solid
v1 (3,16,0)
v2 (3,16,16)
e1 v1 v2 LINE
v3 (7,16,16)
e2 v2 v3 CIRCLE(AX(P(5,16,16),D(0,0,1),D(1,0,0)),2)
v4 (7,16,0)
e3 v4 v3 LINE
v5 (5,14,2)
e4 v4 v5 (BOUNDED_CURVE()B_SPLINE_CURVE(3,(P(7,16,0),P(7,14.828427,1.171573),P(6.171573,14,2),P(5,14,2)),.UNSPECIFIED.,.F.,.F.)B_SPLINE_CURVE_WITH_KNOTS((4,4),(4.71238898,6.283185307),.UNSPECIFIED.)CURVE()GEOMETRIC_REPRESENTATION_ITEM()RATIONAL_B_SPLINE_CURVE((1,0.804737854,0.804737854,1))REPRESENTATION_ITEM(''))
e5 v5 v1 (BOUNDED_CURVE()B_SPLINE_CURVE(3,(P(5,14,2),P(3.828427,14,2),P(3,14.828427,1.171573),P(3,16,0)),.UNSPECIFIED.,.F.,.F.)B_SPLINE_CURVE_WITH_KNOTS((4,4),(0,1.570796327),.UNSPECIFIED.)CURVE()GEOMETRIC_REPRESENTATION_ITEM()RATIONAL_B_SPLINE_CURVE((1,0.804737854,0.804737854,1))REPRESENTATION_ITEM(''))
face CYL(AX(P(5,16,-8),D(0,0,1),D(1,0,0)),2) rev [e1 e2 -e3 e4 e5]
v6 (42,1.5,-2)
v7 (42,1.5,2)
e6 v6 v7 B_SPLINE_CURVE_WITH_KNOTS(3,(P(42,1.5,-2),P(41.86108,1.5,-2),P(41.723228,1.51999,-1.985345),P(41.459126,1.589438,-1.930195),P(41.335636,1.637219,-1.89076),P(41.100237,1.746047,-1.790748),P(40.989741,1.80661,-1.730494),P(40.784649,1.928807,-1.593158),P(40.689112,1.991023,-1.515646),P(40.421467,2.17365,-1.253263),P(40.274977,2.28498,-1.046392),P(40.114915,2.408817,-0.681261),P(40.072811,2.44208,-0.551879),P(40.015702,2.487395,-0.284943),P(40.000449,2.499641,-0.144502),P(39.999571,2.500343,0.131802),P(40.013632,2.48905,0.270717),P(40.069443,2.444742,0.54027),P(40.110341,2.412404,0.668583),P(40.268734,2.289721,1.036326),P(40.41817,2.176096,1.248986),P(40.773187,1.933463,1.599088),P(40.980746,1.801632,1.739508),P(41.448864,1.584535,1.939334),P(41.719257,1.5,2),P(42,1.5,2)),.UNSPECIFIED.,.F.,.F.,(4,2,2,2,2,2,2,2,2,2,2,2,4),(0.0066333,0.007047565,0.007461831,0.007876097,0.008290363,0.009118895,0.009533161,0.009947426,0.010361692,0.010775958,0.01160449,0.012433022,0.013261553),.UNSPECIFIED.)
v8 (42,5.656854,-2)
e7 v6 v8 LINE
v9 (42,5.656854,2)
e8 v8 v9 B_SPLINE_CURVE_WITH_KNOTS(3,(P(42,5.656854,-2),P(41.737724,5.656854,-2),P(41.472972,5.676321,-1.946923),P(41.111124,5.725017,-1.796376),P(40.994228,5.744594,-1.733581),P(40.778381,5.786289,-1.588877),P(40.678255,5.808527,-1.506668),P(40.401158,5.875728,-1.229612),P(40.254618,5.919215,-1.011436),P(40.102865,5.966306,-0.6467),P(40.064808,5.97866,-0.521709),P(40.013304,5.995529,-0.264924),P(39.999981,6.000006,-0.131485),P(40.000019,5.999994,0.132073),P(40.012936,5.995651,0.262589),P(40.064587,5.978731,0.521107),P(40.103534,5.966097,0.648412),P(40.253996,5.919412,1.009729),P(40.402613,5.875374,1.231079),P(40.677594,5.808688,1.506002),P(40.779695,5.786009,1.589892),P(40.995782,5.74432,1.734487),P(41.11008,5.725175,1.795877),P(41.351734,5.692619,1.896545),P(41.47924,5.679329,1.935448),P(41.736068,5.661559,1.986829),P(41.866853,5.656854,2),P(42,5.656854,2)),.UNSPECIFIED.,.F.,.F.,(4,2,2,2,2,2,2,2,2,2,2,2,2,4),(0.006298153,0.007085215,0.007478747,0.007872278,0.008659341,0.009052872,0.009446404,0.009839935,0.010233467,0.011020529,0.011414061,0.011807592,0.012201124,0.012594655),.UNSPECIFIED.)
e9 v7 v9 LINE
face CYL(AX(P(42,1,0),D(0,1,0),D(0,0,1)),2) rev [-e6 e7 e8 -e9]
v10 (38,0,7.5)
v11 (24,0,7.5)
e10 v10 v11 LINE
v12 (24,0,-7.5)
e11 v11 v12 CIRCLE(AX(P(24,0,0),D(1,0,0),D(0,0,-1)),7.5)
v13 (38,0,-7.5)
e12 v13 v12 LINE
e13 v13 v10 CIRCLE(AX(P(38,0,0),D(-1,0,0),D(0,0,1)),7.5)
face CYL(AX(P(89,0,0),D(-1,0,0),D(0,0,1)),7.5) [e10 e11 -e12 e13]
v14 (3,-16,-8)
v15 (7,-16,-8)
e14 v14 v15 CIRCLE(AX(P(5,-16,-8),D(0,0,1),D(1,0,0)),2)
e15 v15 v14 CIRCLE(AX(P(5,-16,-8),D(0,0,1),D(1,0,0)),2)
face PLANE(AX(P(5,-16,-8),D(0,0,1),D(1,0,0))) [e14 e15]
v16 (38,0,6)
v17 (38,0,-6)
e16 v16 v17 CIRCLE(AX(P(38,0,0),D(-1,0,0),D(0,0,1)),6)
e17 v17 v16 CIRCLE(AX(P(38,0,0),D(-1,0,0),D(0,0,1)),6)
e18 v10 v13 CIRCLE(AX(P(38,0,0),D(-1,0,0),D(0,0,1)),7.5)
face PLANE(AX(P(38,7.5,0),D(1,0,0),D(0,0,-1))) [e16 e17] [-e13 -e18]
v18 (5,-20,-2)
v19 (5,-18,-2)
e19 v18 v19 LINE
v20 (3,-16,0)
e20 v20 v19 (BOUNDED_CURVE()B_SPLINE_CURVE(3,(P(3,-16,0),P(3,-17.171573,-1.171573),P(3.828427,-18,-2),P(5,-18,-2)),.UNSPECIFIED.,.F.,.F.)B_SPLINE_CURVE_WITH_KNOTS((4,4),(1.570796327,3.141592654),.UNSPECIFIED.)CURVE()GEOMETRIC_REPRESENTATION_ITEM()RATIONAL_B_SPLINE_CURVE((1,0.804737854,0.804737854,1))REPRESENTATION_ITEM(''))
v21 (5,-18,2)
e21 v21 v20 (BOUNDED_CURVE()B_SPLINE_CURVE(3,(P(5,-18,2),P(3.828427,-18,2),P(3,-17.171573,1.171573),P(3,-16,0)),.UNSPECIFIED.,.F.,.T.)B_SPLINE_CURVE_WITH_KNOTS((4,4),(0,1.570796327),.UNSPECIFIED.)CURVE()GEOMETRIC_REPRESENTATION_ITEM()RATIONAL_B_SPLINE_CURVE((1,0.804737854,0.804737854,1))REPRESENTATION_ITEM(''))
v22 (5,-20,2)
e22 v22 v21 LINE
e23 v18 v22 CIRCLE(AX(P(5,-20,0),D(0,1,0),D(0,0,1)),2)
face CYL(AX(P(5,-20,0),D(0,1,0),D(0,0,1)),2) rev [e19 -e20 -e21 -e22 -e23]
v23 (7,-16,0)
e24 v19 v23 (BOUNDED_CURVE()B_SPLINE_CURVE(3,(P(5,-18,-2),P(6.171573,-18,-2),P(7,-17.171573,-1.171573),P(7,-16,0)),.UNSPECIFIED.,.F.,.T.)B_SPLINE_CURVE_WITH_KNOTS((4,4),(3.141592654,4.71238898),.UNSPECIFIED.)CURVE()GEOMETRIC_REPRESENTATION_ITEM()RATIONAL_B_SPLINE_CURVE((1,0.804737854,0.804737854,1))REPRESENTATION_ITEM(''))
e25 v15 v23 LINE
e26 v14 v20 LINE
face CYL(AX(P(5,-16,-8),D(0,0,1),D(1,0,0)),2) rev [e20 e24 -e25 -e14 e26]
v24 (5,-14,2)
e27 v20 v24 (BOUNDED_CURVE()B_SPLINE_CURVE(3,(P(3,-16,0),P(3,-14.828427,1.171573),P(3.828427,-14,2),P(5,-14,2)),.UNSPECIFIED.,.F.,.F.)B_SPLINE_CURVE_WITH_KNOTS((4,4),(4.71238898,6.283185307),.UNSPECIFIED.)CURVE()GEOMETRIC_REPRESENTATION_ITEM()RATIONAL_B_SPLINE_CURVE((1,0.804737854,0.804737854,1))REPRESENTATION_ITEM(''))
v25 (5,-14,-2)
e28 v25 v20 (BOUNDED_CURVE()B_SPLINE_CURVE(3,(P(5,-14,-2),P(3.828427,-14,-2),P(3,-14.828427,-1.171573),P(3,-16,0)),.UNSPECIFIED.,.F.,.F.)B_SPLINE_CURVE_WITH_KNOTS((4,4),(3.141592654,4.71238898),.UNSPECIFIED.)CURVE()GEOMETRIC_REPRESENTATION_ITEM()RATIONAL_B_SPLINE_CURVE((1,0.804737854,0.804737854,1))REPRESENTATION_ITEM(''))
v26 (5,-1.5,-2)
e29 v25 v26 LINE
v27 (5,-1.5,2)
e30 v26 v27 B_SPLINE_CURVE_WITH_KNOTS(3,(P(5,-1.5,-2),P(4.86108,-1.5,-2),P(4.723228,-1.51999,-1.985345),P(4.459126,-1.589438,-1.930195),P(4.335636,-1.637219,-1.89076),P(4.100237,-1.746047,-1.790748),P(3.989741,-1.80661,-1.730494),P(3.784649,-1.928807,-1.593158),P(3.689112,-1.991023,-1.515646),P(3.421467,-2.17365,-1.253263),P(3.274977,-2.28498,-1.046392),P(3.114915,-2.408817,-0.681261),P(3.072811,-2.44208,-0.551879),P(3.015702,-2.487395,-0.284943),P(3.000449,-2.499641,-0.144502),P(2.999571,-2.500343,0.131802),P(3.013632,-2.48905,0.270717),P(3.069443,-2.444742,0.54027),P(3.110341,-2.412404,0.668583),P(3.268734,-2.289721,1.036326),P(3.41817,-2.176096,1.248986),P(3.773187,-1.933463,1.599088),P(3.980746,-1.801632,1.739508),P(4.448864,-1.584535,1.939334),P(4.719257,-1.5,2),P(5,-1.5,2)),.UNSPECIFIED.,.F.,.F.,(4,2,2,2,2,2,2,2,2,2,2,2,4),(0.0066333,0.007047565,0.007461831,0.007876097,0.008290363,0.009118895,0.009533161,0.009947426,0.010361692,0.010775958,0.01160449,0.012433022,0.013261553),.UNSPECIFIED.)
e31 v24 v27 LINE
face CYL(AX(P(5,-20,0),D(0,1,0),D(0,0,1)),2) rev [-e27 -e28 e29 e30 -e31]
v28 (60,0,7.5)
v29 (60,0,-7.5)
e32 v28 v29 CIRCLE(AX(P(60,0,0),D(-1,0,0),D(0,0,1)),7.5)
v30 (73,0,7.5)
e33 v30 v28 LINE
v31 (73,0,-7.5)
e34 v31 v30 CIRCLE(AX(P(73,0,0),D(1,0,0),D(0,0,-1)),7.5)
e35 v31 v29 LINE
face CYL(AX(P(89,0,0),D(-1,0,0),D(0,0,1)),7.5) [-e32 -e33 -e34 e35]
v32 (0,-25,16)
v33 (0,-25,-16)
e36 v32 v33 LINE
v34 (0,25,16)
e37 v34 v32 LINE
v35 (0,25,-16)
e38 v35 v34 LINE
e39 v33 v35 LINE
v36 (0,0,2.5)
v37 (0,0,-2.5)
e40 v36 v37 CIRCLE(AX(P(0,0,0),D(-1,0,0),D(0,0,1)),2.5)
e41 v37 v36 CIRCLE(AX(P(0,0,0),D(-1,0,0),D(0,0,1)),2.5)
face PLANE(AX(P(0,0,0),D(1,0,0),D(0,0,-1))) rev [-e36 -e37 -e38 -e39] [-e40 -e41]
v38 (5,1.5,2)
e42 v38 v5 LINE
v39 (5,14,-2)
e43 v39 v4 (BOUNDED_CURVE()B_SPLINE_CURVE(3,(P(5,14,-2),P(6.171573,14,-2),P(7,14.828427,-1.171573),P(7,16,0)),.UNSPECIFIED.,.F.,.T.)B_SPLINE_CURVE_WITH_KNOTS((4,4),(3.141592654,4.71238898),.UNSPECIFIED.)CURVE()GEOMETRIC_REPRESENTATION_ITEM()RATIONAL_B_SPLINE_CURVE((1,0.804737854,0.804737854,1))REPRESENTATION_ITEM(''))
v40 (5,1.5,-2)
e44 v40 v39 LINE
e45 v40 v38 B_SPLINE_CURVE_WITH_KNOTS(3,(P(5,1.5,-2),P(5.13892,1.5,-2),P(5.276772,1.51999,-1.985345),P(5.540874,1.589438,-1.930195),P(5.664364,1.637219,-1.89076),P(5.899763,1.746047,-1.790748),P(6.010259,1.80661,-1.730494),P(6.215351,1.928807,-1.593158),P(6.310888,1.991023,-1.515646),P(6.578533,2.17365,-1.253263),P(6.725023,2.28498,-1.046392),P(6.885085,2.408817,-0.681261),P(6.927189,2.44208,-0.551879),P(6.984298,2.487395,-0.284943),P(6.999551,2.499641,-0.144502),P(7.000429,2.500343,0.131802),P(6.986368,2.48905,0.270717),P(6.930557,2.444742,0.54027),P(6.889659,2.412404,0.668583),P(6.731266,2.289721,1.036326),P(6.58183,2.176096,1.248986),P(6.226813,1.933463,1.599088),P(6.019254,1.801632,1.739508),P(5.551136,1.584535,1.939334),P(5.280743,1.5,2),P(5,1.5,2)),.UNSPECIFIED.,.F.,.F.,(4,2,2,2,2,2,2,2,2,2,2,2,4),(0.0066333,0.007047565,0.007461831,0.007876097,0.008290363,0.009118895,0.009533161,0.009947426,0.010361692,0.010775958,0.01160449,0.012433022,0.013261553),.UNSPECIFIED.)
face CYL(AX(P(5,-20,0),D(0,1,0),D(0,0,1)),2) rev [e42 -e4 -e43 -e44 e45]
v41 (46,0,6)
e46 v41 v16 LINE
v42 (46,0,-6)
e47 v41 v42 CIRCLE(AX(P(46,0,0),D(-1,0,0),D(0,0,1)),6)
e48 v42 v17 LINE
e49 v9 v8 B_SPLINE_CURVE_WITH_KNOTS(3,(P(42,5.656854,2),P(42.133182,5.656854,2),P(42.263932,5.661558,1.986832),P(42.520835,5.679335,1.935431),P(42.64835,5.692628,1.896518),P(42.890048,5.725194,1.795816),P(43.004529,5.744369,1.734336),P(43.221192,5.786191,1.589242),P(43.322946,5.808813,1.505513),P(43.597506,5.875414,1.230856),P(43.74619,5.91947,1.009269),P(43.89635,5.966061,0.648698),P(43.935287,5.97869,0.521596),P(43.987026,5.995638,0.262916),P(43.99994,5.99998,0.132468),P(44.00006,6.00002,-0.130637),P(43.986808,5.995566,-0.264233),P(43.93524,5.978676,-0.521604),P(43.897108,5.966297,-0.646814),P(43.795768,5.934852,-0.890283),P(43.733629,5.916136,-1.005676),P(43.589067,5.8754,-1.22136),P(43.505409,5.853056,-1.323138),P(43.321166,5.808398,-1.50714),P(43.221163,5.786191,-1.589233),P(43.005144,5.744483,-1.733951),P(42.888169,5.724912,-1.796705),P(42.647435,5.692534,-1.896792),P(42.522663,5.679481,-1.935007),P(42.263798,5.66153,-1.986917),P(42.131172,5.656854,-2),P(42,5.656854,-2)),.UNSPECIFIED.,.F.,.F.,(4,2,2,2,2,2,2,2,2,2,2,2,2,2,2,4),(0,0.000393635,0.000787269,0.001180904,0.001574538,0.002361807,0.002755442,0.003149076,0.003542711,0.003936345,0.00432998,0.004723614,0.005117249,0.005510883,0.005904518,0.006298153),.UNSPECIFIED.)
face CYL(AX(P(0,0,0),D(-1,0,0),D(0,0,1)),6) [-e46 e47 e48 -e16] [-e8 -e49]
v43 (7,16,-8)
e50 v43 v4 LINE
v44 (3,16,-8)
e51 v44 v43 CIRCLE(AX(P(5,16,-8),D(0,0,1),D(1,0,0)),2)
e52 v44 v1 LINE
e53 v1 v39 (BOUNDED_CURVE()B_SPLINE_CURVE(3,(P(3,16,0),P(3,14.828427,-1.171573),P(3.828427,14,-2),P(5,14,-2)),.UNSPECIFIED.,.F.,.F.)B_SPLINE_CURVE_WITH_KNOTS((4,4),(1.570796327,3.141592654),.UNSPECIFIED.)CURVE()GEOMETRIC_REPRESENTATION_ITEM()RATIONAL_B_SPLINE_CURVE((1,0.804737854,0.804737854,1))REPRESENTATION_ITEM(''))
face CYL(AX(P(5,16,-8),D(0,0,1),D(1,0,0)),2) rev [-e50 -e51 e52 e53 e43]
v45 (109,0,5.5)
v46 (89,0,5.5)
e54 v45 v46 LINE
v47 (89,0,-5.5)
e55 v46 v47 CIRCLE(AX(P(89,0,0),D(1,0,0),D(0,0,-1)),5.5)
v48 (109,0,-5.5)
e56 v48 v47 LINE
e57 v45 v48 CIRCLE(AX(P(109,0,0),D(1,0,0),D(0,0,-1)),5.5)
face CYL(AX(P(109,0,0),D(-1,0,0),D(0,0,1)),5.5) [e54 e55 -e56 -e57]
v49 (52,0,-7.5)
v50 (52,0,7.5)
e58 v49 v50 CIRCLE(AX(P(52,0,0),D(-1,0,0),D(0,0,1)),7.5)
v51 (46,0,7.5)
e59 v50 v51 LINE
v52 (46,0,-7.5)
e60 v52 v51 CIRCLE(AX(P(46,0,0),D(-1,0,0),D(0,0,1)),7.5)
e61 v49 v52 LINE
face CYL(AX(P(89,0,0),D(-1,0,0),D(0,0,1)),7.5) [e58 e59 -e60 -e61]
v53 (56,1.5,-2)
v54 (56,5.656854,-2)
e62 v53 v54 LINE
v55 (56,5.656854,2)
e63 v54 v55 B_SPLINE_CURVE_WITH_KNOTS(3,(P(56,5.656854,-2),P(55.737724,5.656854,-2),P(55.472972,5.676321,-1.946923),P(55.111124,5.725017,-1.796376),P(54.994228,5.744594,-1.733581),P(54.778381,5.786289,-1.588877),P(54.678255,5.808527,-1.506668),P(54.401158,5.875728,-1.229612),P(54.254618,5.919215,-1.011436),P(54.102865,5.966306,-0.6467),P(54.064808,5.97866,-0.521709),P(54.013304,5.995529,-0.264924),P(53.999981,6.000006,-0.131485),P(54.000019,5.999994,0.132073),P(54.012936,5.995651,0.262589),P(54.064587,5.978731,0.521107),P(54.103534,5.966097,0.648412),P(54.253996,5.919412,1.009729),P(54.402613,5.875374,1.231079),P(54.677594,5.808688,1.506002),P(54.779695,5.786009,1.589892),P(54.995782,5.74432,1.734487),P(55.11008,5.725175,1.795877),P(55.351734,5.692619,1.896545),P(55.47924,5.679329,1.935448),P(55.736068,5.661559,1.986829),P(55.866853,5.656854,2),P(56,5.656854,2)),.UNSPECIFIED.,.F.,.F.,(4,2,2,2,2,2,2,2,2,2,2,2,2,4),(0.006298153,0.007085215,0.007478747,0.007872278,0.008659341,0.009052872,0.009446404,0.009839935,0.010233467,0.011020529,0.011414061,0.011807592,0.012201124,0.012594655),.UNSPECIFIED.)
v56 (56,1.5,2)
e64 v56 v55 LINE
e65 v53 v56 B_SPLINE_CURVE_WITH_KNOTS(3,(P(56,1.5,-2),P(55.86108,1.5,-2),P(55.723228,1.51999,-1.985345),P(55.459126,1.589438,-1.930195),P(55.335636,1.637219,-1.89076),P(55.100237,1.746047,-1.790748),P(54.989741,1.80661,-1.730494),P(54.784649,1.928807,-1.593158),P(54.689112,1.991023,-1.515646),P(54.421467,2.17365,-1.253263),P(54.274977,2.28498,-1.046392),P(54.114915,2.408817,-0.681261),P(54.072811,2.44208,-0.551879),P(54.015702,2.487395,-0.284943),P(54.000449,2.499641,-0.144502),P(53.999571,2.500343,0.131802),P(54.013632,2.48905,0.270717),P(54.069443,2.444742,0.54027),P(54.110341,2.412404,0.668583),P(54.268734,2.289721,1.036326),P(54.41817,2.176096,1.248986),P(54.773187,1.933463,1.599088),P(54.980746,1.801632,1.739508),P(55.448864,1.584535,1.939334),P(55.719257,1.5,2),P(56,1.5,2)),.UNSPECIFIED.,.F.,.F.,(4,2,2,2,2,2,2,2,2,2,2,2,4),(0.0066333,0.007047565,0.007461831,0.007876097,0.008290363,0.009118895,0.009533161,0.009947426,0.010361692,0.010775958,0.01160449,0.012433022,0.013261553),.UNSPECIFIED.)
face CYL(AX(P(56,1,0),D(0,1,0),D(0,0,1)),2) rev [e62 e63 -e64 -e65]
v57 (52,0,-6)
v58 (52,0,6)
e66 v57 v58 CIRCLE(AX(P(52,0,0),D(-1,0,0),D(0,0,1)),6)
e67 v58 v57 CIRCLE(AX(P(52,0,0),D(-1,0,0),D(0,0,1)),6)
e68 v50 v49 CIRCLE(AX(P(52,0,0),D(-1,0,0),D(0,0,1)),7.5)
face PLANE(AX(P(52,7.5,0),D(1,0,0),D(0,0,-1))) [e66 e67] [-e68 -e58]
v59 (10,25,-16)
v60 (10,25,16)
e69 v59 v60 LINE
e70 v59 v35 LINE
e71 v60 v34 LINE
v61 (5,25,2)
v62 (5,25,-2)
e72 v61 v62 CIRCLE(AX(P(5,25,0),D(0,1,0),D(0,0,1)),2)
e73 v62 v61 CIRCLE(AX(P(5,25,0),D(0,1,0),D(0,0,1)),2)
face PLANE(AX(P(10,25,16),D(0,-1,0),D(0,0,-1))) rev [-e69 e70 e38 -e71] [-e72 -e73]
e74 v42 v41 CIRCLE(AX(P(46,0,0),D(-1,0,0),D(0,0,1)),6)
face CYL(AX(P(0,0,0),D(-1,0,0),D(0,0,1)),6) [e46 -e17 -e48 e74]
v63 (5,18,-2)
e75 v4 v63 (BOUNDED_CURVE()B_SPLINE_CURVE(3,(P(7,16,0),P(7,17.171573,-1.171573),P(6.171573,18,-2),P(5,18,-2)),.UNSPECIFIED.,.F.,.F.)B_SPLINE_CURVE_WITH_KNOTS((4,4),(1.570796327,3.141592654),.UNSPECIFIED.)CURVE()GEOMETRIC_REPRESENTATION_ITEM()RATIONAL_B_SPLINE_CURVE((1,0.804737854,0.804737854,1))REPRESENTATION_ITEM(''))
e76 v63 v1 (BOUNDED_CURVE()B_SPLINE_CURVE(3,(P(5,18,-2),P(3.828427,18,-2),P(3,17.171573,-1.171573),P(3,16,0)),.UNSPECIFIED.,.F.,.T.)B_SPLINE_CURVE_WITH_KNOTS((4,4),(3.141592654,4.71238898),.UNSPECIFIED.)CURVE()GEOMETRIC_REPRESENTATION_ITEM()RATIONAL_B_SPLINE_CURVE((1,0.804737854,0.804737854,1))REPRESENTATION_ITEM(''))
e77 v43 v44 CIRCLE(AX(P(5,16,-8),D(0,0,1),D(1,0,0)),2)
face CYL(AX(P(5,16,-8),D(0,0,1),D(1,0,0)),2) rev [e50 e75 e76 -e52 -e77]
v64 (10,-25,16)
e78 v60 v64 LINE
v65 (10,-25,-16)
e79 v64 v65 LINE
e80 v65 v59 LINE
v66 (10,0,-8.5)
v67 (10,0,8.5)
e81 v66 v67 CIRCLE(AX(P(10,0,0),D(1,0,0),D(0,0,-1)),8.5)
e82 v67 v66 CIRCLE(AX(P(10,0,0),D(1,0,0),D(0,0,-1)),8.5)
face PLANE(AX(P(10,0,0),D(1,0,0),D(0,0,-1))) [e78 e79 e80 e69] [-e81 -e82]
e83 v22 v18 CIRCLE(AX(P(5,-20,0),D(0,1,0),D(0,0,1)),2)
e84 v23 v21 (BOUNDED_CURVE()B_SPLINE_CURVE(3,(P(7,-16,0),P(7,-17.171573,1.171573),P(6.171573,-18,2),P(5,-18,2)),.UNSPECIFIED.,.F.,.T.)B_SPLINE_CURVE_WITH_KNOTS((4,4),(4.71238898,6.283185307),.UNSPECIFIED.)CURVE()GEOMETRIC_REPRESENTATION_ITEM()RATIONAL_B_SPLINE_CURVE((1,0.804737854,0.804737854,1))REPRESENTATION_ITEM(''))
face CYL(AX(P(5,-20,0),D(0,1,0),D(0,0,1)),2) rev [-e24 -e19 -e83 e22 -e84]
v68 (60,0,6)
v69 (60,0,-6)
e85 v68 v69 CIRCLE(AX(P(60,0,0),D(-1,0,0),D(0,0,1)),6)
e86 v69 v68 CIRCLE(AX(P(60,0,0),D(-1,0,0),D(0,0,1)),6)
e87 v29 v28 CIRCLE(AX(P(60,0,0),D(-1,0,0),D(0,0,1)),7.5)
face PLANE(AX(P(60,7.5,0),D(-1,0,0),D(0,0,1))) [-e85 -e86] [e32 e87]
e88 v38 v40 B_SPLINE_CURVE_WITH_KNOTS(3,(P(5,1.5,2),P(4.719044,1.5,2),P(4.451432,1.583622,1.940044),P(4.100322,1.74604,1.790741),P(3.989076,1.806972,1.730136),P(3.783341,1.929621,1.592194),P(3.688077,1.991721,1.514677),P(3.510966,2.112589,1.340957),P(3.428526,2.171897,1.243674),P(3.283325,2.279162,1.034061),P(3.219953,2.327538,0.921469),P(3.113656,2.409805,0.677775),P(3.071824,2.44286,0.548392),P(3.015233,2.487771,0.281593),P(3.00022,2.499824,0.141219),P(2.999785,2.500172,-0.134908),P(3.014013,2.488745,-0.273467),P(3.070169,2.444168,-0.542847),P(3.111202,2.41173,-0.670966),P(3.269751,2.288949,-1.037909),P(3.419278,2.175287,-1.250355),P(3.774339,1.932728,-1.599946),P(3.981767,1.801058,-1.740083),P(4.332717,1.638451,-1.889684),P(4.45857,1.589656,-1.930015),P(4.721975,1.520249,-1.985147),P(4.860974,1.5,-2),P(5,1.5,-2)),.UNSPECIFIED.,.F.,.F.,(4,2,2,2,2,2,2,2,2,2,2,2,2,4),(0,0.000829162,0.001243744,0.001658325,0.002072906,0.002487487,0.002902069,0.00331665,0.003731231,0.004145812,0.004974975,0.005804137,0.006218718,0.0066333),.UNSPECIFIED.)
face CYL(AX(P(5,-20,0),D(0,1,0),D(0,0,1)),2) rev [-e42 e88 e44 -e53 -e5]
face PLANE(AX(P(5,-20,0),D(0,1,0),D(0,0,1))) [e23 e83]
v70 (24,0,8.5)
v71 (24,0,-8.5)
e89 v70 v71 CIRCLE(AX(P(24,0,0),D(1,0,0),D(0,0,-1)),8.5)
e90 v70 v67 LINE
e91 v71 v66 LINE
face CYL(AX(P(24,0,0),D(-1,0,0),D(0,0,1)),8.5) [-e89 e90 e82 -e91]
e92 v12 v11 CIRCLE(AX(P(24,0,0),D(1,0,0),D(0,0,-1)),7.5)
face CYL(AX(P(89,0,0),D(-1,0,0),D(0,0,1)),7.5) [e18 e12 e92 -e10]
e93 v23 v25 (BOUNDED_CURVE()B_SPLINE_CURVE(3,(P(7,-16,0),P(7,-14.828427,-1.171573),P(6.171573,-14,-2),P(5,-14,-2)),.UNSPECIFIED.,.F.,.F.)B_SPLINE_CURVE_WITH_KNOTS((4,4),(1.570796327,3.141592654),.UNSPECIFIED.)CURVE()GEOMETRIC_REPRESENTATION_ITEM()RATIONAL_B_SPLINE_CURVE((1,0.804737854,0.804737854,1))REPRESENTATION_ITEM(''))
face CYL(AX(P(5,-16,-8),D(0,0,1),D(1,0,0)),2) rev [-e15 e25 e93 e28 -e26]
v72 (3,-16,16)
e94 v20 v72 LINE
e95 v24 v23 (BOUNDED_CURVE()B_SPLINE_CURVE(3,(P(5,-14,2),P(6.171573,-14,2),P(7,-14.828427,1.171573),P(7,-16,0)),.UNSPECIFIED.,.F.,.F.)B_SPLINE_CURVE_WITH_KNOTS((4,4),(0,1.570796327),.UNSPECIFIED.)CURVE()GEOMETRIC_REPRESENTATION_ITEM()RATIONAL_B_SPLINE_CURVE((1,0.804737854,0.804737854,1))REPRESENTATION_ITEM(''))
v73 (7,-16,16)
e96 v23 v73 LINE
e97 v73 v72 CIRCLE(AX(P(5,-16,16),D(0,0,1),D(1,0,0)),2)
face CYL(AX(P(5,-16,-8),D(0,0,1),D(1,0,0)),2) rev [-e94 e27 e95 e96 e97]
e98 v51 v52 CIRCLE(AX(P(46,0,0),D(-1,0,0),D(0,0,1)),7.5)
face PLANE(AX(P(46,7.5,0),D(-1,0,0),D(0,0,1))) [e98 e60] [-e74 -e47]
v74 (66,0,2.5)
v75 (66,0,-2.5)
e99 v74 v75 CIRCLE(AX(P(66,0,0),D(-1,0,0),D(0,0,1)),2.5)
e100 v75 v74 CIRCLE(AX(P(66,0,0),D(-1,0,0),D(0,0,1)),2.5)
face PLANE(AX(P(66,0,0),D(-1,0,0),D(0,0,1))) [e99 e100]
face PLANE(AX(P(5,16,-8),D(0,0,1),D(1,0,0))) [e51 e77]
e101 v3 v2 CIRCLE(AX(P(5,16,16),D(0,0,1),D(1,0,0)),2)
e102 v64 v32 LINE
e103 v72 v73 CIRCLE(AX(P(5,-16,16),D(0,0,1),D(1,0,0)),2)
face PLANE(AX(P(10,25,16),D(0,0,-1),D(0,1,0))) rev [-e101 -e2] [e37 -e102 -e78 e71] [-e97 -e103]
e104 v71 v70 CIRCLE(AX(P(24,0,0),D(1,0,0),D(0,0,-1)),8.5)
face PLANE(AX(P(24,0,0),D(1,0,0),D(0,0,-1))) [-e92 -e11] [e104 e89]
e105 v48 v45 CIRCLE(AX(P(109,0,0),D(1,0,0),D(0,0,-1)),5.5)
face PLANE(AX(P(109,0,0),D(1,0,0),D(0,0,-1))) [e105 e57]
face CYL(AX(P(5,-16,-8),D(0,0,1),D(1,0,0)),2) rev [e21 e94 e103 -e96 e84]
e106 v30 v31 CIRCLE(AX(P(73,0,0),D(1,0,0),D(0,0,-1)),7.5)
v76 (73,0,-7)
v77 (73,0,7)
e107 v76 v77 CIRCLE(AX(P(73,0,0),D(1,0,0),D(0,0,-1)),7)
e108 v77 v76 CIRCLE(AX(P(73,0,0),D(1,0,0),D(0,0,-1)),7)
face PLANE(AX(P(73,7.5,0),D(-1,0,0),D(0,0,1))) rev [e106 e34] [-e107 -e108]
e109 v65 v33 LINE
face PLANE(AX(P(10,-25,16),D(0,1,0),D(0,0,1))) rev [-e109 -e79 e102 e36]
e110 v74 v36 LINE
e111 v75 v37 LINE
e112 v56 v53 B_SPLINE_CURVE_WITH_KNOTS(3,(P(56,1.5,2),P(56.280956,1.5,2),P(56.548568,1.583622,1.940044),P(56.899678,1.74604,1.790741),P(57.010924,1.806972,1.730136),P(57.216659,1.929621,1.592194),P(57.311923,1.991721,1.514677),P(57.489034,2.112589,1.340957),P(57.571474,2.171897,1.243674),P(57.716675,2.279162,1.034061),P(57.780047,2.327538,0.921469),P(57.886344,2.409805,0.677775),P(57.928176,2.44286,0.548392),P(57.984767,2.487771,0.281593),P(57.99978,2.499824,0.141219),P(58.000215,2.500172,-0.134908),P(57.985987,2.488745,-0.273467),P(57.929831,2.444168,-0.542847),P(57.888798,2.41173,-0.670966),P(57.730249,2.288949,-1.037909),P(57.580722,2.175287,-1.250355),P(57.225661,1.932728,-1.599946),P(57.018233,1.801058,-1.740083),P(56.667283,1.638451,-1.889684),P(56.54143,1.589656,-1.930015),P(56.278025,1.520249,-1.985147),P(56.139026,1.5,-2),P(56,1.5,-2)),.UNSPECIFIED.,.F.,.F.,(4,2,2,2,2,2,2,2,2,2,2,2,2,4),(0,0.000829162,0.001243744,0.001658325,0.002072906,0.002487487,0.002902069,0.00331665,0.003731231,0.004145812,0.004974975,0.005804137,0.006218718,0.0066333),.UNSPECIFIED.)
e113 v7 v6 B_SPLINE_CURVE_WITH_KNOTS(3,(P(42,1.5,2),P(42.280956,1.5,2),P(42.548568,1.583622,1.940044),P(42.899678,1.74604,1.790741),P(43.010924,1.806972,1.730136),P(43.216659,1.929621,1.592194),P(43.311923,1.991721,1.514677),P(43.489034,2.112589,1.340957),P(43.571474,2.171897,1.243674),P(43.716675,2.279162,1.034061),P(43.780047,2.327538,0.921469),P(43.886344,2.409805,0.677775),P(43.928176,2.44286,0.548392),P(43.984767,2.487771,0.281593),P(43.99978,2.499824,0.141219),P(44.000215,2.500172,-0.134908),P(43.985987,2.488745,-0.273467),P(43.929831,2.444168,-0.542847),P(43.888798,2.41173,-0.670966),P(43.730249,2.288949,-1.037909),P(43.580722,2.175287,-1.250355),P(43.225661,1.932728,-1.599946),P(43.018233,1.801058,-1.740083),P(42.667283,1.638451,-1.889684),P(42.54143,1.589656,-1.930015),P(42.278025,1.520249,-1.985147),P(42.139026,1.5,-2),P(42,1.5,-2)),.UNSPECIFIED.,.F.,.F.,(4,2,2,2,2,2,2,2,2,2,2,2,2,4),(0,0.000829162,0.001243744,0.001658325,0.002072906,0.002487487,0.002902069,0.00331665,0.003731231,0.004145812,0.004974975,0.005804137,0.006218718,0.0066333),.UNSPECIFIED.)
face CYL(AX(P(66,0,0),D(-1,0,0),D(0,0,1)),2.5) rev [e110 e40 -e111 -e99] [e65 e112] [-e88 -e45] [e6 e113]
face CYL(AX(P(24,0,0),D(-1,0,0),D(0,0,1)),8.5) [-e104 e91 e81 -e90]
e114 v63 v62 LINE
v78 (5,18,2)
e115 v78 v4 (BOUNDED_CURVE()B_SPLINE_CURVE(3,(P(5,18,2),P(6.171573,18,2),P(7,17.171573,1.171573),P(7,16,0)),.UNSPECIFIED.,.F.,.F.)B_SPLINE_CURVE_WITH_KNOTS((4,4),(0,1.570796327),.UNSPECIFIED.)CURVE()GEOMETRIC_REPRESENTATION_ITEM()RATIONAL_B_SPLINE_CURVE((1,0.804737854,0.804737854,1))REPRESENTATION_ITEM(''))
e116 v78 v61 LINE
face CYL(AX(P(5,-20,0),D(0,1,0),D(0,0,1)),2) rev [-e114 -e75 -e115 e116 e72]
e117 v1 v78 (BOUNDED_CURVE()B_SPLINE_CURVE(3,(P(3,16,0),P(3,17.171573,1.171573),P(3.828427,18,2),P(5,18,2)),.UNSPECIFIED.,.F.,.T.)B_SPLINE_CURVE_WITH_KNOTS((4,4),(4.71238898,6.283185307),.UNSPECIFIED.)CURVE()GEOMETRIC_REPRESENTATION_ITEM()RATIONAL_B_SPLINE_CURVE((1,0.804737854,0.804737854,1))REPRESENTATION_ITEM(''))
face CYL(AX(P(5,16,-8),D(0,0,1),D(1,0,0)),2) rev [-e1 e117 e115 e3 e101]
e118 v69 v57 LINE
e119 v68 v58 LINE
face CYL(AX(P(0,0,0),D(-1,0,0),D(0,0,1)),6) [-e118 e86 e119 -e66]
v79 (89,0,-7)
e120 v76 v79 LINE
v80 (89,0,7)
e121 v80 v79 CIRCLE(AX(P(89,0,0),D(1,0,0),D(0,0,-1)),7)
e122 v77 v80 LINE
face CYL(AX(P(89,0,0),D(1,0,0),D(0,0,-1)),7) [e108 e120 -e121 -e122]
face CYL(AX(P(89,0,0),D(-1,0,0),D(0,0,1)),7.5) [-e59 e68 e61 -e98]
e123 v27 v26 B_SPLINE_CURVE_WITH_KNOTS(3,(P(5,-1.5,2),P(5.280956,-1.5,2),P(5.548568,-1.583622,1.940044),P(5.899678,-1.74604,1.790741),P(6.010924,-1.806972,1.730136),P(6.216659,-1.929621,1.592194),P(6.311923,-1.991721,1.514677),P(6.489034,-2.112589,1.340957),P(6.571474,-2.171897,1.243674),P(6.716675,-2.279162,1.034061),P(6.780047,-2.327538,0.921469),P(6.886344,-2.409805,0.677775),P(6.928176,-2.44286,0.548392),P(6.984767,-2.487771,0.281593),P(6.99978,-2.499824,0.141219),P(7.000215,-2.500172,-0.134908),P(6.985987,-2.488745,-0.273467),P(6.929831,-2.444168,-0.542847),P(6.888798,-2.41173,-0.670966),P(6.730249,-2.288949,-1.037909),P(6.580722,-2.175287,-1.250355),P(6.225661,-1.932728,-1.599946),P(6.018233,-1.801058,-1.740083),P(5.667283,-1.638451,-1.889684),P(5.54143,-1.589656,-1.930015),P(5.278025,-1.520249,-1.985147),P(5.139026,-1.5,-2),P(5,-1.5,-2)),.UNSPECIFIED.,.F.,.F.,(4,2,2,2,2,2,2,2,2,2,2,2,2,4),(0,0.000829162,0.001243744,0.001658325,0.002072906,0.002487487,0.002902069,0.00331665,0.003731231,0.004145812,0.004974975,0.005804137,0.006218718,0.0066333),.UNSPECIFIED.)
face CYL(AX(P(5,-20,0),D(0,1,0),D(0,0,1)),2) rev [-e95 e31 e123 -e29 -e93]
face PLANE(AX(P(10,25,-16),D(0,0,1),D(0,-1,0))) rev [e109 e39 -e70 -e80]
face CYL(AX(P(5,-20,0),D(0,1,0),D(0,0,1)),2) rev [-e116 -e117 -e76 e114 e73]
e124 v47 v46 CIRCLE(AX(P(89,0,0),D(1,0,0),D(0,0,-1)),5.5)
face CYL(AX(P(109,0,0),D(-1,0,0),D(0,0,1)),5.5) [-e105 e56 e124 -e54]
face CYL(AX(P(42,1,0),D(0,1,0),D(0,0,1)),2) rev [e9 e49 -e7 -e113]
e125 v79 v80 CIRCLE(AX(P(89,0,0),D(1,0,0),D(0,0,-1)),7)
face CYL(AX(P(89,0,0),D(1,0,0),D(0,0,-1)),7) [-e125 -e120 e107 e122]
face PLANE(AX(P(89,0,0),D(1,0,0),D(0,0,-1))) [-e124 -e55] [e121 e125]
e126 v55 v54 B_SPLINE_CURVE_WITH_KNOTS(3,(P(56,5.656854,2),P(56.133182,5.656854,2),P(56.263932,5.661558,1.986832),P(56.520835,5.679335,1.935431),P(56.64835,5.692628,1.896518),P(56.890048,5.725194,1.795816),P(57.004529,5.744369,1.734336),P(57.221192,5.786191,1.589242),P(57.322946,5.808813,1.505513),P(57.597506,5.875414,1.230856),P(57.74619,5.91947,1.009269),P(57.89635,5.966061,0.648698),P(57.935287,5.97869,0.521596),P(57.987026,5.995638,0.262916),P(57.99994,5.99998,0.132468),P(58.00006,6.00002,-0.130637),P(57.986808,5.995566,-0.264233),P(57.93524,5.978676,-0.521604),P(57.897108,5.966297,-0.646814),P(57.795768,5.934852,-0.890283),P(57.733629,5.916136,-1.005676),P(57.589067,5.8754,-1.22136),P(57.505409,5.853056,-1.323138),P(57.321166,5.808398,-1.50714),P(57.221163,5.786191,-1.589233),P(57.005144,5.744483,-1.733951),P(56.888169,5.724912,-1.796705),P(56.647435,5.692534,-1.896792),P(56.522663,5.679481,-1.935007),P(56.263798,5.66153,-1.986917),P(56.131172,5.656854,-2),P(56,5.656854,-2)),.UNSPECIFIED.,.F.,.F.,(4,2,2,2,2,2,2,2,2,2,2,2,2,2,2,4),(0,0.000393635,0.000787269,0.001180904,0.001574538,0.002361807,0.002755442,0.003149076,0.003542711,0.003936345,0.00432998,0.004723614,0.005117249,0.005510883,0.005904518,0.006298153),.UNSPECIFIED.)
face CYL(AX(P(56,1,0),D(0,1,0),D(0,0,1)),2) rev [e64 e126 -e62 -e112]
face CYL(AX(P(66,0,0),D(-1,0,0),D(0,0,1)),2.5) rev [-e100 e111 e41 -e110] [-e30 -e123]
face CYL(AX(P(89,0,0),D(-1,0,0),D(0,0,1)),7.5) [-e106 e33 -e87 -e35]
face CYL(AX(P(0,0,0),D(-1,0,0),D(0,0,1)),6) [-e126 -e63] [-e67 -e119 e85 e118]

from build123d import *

# Parameters (mm, degrees)
SKETCH1_W           = 32
SKETCH1_H           = 50
BOSS_EXTRUDE1_DEPTH = 10
SKETCH2_R           = 8.5
BOSS_EXTRUDE2_DEPTH = 14
SKETCH3_R           = 2
CUT_EXTRUDE1_DEPTH  = 24
SKETCH4_R           = 2
CUT_EXTRUDE2_DEPTH  = 45
SKETCH5_R           = 7.5
BOSS_EXTRUDE3_DEPTH = 65
SKETCH6_W           = 8
SKETCH6_H           = 1.5
SKETCH7_R           = 5.5
BOSS_EXTRUDE4_DEPTH = 20
SKETCH9_W           = 16
SKETCH9_H           = 0.5
SKETCH10_R          = 2.5
CUT_EXTRUDE3_DEPTH  = 66
SKETCH11_R          = 2
CUT_EXTRUDE4_DEPTH  = 24


with BuildPart() as part:
    # Sketch1 → Boss-Extrude1 (new body)
    with BuildSketch(Plane(origin=(0, 0, 0), x_dir=(0, 0, -1), z_dir=(1, 0, 0))):
        Rectangle(SKETCH1_W, SKETCH1_H)
    extrude(amount=BOSS_EXTRUDE1_DEPTH)

    # Sketch2 → Boss-Extrude2 (add)
    with BuildSketch(Plane(origin=(10, 0, 0), x_dir=(0, 0, -1), z_dir=(1, 0, 0))):
        Circle(SKETCH2_R)
    extrude(amount=BOSS_EXTRUDE2_DEPTH)

    # Sketch3 → Cut-Extrude1 (cut)
    with BuildSketch(Plane.XY.offset(16)):
        with Locations((5, 16)):
            Circle(SKETCH3_R)
        with Locations((5, -16)):
            Circle(SKETCH3_R)
    extrude(amount=-CUT_EXTRUDE1_DEPTH, mode=Mode.SUBTRACT)

    # Sketch4 → Cut-Extrude2 (cut)
    with BuildSketch(Plane(origin=(0, 25, 0), x_dir=(1, 0, 0), z_dir=(0, 1, 0))):
        with Locations(Location((5, 0, 0), (0, 0, 270))):
            Circle(SKETCH4_R)
    extrude(amount=-CUT_EXTRUDE2_DEPTH, mode=Mode.SUBTRACT)

    # Sketch5 → Boss-Extrude3 (add)
    with BuildSketch(Plane(origin=(24, 0, 0), x_dir=(0, 0, -1), z_dir=(1, 0, 0))):
        Circle(SKETCH5_R)
    extrude(amount=BOSS_EXTRUDE3_DEPTH)

    # Sketch6 → Cut-Revolve1 (revolve, cut)
    with BuildSketch(Plane.XY, mode=Mode.PRIVATE) as cut_revolve1_sk:
        with Locations((42, 6.75)):
            Rectangle(SKETCH6_W, SKETCH6_H)
        with Locations((56, 6.75)):
            Rectangle(SKETCH6_W, SKETCH6_H)
    revolve(cut_revolve1_sk.sketch.rotate(Axis((0, 0, 0), (1, 0, 0)), 90), axis=Axis((0, 0, 0), (1, 0, 0)), mode=Mode.SUBTRACT)

    # Sketch7 → Boss-Extrude4 (add)
    with BuildSketch(Plane(origin=(89, 0, 0), x_dir=(0, 0, -1), z_dir=(1, 0, 0))):
        Circle(SKETCH7_R)
    extrude(amount=BOSS_EXTRUDE4_DEPTH)

    # Sketch9 → Cut-Revolve2 (revolve, cut)
    with BuildSketch(Plane.XY, mode=Mode.PRIVATE) as cut_revolve2_sk:
        with Locations((81, 7.25)):
            Rectangle(SKETCH9_W, SKETCH9_H)
    revolve(cut_revolve2_sk.sketch.rotate(Axis((89, 0, 0), (-1, 0, 0)), 270), axis=Axis((89, 0, 0), (-1, 0, 0)), mode=Mode.SUBTRACT)

    # Sketch10 → Cut-Extrude3 (cut)
    with BuildSketch(Plane.ZY):
        Circle(SKETCH10_R)
    extrude(amount=-CUT_EXTRUDE3_DEPTH, mode=Mode.SUBTRACT)

    # Sketch11 → Cut-Extrude4 (cut)
    with BuildSketch(Plane(origin=(0, 25, 0), x_dir=(1, 0, 0), z_dir=(0, 1, 0))):
        with Locations(Location((42, 0, 0), (0, 0, 270))):
            Circle(SKETCH11_R)
        with Locations(Location((56, 0, 0), (0, 0, 270))):
            Circle(SKETCH11_R)
    extrude(amount=-CUT_EXTRUDE4_DEPTH, mode=Mode.SUBTRACT)


solid = part.part
